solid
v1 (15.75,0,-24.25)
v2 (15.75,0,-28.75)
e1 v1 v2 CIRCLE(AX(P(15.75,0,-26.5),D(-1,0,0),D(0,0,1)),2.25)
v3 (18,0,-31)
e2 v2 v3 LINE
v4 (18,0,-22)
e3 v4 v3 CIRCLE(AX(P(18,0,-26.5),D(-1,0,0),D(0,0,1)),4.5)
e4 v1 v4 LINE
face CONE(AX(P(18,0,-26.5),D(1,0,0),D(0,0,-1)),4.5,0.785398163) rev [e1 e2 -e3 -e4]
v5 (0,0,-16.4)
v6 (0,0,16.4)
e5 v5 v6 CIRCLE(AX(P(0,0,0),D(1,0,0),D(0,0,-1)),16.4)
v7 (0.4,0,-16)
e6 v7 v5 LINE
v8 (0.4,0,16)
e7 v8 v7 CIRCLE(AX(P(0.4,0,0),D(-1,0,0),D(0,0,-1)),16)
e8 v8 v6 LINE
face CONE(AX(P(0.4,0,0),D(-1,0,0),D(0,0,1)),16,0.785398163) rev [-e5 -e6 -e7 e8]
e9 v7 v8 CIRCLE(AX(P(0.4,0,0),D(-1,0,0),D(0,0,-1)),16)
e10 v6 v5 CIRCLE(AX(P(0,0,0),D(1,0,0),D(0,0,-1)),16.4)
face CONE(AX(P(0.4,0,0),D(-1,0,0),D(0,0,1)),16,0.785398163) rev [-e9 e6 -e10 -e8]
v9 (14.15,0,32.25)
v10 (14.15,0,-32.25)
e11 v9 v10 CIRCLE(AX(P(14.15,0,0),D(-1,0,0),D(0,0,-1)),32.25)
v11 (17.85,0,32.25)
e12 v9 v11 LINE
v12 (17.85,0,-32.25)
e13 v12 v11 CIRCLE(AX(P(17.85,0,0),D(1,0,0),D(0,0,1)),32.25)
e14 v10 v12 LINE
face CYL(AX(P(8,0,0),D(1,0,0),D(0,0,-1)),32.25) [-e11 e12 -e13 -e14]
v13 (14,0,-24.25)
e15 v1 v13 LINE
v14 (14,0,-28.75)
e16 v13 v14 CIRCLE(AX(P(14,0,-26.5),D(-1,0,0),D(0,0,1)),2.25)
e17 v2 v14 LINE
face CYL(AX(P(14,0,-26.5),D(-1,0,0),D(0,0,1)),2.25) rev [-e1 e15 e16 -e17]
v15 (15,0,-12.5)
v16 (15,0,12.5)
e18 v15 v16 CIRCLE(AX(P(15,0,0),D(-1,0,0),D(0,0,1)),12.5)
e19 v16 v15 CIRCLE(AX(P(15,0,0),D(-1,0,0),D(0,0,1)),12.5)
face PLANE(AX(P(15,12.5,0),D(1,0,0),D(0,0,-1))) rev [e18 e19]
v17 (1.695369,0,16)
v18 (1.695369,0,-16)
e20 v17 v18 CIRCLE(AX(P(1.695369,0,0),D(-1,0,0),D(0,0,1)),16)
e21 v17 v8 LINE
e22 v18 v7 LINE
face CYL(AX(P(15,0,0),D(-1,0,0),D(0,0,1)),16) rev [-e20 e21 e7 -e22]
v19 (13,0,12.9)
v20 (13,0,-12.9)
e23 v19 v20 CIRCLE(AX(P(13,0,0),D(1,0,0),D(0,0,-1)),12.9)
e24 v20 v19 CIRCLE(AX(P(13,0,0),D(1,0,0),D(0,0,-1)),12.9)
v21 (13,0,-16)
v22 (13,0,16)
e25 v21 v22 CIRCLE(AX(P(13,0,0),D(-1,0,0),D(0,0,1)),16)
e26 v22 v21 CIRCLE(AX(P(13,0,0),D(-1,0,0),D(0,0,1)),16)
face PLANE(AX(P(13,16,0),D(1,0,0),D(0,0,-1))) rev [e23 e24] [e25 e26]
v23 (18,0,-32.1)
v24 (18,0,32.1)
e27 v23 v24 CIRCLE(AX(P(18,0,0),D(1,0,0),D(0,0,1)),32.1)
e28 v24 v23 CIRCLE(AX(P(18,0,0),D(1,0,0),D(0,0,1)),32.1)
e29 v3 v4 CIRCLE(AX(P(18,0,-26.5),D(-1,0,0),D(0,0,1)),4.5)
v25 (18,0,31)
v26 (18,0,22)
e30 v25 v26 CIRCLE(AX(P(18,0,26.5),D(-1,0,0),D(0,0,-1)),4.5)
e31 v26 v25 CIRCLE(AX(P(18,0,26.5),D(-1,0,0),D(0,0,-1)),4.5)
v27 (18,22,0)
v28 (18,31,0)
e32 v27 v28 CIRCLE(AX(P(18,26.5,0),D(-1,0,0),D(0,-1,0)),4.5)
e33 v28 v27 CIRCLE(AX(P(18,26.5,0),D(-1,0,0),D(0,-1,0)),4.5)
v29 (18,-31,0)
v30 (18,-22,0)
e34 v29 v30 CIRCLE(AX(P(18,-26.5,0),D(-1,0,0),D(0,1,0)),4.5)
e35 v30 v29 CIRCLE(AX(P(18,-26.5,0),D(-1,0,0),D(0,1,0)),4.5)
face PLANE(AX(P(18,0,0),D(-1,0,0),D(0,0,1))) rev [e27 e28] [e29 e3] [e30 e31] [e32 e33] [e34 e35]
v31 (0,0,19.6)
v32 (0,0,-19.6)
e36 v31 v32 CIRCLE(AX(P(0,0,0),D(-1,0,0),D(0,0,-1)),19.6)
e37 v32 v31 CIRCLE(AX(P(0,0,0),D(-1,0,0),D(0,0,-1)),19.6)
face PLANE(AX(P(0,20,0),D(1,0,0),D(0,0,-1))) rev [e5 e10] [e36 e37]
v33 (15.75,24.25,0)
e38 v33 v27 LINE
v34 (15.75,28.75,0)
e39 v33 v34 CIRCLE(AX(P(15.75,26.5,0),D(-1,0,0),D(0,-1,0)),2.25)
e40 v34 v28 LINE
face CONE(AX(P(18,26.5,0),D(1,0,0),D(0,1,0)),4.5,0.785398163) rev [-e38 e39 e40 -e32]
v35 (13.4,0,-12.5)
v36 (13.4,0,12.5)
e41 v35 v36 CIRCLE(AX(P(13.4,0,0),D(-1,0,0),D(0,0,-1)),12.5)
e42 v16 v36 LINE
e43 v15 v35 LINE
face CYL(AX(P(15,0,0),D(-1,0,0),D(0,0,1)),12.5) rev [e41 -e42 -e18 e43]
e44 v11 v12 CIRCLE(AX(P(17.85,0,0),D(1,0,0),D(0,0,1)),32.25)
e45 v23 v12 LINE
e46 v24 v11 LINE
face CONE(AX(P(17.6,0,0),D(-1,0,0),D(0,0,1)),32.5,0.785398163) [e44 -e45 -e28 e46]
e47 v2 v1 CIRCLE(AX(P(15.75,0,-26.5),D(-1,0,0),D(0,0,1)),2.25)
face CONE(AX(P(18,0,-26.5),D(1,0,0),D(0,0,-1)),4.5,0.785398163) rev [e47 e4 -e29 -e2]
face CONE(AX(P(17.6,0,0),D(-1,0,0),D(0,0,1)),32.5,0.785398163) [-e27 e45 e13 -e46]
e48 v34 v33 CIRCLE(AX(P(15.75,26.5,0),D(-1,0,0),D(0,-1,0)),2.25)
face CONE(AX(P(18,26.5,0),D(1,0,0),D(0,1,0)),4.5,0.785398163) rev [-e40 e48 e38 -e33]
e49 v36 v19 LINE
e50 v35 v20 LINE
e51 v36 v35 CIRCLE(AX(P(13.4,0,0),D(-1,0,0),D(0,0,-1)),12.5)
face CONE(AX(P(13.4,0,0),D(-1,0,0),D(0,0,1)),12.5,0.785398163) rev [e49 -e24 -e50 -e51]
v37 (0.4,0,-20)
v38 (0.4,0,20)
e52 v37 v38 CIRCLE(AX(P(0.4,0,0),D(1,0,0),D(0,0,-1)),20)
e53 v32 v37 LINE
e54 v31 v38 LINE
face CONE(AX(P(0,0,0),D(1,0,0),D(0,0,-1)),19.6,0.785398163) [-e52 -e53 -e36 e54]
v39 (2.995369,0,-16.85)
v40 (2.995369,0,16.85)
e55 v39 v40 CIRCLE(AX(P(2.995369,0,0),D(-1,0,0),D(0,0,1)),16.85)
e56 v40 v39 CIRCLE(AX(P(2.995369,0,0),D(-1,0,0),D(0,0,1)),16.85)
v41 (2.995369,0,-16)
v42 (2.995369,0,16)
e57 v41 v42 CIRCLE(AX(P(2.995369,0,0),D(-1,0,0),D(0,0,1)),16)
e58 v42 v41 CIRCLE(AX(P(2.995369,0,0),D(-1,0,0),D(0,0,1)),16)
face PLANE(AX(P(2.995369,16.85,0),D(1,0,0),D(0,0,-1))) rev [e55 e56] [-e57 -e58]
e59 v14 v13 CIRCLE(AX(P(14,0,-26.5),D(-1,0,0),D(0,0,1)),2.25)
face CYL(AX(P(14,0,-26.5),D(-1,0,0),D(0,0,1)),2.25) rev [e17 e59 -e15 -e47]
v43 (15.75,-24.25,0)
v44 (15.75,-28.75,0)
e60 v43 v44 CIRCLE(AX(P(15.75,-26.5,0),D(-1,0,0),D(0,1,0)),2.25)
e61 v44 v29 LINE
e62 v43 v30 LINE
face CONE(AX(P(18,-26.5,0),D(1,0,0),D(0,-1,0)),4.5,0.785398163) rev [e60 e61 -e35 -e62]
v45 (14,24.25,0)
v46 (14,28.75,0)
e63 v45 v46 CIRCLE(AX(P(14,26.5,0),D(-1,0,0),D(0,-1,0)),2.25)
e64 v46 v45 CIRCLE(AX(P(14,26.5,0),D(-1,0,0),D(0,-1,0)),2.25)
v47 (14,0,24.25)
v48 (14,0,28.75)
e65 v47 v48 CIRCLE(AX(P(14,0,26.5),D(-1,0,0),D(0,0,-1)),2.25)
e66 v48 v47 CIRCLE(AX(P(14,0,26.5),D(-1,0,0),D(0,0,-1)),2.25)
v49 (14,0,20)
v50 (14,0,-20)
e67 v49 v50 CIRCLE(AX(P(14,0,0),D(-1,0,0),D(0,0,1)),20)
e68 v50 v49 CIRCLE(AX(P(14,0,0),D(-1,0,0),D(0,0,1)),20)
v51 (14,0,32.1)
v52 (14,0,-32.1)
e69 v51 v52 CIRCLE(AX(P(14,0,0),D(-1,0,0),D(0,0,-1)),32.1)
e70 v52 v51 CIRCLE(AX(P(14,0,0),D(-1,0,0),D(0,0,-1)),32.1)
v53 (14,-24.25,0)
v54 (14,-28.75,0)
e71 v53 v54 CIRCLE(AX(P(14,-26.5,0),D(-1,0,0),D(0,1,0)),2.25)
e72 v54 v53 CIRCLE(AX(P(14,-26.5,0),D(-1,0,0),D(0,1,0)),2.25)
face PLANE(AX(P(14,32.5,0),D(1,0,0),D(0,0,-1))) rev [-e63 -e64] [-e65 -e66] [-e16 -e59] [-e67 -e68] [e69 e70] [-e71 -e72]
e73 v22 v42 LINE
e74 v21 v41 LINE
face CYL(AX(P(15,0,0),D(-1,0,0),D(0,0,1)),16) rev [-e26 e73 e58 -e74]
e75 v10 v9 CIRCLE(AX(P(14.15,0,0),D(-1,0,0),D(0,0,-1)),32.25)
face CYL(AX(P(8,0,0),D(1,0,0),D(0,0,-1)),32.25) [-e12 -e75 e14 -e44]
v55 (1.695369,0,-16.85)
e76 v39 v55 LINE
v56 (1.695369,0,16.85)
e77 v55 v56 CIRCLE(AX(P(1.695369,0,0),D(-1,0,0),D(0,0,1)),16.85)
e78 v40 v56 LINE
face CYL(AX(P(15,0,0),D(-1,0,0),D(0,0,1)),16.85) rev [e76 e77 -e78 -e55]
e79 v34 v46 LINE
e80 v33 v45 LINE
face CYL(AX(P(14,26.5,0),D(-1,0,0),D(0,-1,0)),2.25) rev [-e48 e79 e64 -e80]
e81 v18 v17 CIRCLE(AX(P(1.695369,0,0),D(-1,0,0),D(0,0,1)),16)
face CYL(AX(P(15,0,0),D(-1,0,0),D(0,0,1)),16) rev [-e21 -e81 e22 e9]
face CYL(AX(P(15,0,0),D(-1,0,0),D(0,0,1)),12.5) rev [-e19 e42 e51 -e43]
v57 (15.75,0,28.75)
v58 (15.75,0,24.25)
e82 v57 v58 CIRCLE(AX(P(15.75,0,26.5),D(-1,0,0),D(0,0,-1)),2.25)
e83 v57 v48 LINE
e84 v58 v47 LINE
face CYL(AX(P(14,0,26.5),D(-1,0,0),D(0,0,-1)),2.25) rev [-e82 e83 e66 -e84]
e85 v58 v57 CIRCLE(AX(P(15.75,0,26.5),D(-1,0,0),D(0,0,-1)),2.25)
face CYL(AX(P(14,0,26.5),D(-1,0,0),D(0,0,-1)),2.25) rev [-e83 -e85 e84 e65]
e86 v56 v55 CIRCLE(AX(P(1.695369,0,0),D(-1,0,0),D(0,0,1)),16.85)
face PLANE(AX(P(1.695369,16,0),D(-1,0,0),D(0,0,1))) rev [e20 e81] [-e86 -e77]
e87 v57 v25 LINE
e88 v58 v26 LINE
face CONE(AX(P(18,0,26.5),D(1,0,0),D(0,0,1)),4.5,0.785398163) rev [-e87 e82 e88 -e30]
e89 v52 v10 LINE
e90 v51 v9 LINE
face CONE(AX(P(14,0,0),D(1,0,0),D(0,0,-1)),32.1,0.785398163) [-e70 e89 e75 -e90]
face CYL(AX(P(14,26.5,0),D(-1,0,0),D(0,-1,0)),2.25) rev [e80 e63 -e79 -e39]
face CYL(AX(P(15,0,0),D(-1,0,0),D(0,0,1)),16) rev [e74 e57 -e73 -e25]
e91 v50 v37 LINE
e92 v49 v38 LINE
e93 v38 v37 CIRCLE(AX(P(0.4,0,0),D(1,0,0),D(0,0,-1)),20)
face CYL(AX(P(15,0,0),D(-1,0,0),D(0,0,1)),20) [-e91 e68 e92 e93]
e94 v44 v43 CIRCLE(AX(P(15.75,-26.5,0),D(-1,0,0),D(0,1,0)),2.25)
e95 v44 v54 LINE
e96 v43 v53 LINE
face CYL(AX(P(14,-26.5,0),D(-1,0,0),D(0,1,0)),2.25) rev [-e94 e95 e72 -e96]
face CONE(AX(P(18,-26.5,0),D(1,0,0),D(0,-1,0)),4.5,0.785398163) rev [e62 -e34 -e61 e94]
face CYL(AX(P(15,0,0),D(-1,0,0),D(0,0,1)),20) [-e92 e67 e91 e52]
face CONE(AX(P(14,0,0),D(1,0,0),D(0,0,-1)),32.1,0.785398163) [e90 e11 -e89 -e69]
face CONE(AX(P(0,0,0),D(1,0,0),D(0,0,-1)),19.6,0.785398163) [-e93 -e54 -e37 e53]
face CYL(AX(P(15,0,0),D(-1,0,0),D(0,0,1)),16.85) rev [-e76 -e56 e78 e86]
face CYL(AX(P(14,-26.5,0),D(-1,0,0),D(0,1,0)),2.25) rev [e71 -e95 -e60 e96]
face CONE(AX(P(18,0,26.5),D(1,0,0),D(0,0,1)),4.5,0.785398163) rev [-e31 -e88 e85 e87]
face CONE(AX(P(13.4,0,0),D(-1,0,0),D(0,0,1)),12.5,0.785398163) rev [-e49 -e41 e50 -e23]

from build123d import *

# Parameters (mm, degrees)
CIRPATTERN1_COUNT  = 4
CHAMFER1_SIZE      = 0.4
CUT_EXTRUDE1_START = -10
SKETCH6_R          = 32.5
SKETCH6_R_2        = 32.25
CUT_EXTRUDE1_DEPTH = 10


with BuildPart() as part:
    # Sketch1 → Revolve1 (revolve)
    with BuildSketch(Plane.XY, mode=Mode.PRIVATE) as revolve1_sk:
        Polygon((0, 16), (1.695369244, 16), (1.695369244, 16.85), (2.995369244, 16.85), (2.995369244, 16), (13, 16), (13, 12.5), (15, 12.5), (15, 0), (18, 0), (18, 32.5), (14, 32.5), (14, 20), (0, 20), align=None)
    revolve(revolve1_sk.sketch.rotate(Axis((15, 0, 0), (1, 0, 0)), 90), axis=Axis((15, 0, 0), (1, 0, 0)))

    # Sketch2 → Cut-Revolve1 (revolve, cut)
    with BuildSketch(Plane(origin=(0, 0, 0), x_dir=(1, 0, 0), z_dir=(0, 1, 0)), mode=Mode.PRIVATE) as cut_revolve1_sk:
        Polygon((14, 26.5), (18, 26.5), (18, 31), (15.75, 28.75), (14, 28.75), align=None)
    cut_revolve1 = revolve(cut_revolve1_sk.sketch.rotate(Axis((14, 0, -26.5), (1, 0, 0)), 180), axis=Axis((14, 0, -26.5), (1, 0, 0)), mode=Mode.SUBTRACT)

    # CirPattern1: Cut-Revolve1 ×4 about axis
    cirpattern1_axis = Axis((0, 0, 0), (1, 0, 0))
    for i in range(1, CIRPATTERN1_COUNT):
        add(cut_revolve1.rotate(cirpattern1_axis, i * 360 / CIRPATTERN1_COUNT), mode=Mode.SUBTRACT)

    # Chamfer1
    chamfer1_edges = [part.edges().sort_by_distance(p)[0] for p in [
        (14, 0, -32.5),
        (18, 0, -32.5),
        (13, 0, -12.5),
        (0, 0, -16),
        (0, 0, -20),
    ]]
    chamfer(chamfer1_edges, length=CHAMFER1_SIZE)

    # Sketch6 → Cut-Extrude1 (cut)
    with BuildSketch(Plane(origin=(18, 0, 0), x_dir=(0, 0, -1), z_dir=(1, 0, 0)).offset(CUT_EXTRUDE1_START)):
        Circle(SKETCH6_R)
        Circle(SKETCH6_R_2, mode=Mode.SUBTRACT)
    extrude(amount=CUT_EXTRUDE1_DEPTH, mode=Mode.SUBTRACT)


solid = part.part
